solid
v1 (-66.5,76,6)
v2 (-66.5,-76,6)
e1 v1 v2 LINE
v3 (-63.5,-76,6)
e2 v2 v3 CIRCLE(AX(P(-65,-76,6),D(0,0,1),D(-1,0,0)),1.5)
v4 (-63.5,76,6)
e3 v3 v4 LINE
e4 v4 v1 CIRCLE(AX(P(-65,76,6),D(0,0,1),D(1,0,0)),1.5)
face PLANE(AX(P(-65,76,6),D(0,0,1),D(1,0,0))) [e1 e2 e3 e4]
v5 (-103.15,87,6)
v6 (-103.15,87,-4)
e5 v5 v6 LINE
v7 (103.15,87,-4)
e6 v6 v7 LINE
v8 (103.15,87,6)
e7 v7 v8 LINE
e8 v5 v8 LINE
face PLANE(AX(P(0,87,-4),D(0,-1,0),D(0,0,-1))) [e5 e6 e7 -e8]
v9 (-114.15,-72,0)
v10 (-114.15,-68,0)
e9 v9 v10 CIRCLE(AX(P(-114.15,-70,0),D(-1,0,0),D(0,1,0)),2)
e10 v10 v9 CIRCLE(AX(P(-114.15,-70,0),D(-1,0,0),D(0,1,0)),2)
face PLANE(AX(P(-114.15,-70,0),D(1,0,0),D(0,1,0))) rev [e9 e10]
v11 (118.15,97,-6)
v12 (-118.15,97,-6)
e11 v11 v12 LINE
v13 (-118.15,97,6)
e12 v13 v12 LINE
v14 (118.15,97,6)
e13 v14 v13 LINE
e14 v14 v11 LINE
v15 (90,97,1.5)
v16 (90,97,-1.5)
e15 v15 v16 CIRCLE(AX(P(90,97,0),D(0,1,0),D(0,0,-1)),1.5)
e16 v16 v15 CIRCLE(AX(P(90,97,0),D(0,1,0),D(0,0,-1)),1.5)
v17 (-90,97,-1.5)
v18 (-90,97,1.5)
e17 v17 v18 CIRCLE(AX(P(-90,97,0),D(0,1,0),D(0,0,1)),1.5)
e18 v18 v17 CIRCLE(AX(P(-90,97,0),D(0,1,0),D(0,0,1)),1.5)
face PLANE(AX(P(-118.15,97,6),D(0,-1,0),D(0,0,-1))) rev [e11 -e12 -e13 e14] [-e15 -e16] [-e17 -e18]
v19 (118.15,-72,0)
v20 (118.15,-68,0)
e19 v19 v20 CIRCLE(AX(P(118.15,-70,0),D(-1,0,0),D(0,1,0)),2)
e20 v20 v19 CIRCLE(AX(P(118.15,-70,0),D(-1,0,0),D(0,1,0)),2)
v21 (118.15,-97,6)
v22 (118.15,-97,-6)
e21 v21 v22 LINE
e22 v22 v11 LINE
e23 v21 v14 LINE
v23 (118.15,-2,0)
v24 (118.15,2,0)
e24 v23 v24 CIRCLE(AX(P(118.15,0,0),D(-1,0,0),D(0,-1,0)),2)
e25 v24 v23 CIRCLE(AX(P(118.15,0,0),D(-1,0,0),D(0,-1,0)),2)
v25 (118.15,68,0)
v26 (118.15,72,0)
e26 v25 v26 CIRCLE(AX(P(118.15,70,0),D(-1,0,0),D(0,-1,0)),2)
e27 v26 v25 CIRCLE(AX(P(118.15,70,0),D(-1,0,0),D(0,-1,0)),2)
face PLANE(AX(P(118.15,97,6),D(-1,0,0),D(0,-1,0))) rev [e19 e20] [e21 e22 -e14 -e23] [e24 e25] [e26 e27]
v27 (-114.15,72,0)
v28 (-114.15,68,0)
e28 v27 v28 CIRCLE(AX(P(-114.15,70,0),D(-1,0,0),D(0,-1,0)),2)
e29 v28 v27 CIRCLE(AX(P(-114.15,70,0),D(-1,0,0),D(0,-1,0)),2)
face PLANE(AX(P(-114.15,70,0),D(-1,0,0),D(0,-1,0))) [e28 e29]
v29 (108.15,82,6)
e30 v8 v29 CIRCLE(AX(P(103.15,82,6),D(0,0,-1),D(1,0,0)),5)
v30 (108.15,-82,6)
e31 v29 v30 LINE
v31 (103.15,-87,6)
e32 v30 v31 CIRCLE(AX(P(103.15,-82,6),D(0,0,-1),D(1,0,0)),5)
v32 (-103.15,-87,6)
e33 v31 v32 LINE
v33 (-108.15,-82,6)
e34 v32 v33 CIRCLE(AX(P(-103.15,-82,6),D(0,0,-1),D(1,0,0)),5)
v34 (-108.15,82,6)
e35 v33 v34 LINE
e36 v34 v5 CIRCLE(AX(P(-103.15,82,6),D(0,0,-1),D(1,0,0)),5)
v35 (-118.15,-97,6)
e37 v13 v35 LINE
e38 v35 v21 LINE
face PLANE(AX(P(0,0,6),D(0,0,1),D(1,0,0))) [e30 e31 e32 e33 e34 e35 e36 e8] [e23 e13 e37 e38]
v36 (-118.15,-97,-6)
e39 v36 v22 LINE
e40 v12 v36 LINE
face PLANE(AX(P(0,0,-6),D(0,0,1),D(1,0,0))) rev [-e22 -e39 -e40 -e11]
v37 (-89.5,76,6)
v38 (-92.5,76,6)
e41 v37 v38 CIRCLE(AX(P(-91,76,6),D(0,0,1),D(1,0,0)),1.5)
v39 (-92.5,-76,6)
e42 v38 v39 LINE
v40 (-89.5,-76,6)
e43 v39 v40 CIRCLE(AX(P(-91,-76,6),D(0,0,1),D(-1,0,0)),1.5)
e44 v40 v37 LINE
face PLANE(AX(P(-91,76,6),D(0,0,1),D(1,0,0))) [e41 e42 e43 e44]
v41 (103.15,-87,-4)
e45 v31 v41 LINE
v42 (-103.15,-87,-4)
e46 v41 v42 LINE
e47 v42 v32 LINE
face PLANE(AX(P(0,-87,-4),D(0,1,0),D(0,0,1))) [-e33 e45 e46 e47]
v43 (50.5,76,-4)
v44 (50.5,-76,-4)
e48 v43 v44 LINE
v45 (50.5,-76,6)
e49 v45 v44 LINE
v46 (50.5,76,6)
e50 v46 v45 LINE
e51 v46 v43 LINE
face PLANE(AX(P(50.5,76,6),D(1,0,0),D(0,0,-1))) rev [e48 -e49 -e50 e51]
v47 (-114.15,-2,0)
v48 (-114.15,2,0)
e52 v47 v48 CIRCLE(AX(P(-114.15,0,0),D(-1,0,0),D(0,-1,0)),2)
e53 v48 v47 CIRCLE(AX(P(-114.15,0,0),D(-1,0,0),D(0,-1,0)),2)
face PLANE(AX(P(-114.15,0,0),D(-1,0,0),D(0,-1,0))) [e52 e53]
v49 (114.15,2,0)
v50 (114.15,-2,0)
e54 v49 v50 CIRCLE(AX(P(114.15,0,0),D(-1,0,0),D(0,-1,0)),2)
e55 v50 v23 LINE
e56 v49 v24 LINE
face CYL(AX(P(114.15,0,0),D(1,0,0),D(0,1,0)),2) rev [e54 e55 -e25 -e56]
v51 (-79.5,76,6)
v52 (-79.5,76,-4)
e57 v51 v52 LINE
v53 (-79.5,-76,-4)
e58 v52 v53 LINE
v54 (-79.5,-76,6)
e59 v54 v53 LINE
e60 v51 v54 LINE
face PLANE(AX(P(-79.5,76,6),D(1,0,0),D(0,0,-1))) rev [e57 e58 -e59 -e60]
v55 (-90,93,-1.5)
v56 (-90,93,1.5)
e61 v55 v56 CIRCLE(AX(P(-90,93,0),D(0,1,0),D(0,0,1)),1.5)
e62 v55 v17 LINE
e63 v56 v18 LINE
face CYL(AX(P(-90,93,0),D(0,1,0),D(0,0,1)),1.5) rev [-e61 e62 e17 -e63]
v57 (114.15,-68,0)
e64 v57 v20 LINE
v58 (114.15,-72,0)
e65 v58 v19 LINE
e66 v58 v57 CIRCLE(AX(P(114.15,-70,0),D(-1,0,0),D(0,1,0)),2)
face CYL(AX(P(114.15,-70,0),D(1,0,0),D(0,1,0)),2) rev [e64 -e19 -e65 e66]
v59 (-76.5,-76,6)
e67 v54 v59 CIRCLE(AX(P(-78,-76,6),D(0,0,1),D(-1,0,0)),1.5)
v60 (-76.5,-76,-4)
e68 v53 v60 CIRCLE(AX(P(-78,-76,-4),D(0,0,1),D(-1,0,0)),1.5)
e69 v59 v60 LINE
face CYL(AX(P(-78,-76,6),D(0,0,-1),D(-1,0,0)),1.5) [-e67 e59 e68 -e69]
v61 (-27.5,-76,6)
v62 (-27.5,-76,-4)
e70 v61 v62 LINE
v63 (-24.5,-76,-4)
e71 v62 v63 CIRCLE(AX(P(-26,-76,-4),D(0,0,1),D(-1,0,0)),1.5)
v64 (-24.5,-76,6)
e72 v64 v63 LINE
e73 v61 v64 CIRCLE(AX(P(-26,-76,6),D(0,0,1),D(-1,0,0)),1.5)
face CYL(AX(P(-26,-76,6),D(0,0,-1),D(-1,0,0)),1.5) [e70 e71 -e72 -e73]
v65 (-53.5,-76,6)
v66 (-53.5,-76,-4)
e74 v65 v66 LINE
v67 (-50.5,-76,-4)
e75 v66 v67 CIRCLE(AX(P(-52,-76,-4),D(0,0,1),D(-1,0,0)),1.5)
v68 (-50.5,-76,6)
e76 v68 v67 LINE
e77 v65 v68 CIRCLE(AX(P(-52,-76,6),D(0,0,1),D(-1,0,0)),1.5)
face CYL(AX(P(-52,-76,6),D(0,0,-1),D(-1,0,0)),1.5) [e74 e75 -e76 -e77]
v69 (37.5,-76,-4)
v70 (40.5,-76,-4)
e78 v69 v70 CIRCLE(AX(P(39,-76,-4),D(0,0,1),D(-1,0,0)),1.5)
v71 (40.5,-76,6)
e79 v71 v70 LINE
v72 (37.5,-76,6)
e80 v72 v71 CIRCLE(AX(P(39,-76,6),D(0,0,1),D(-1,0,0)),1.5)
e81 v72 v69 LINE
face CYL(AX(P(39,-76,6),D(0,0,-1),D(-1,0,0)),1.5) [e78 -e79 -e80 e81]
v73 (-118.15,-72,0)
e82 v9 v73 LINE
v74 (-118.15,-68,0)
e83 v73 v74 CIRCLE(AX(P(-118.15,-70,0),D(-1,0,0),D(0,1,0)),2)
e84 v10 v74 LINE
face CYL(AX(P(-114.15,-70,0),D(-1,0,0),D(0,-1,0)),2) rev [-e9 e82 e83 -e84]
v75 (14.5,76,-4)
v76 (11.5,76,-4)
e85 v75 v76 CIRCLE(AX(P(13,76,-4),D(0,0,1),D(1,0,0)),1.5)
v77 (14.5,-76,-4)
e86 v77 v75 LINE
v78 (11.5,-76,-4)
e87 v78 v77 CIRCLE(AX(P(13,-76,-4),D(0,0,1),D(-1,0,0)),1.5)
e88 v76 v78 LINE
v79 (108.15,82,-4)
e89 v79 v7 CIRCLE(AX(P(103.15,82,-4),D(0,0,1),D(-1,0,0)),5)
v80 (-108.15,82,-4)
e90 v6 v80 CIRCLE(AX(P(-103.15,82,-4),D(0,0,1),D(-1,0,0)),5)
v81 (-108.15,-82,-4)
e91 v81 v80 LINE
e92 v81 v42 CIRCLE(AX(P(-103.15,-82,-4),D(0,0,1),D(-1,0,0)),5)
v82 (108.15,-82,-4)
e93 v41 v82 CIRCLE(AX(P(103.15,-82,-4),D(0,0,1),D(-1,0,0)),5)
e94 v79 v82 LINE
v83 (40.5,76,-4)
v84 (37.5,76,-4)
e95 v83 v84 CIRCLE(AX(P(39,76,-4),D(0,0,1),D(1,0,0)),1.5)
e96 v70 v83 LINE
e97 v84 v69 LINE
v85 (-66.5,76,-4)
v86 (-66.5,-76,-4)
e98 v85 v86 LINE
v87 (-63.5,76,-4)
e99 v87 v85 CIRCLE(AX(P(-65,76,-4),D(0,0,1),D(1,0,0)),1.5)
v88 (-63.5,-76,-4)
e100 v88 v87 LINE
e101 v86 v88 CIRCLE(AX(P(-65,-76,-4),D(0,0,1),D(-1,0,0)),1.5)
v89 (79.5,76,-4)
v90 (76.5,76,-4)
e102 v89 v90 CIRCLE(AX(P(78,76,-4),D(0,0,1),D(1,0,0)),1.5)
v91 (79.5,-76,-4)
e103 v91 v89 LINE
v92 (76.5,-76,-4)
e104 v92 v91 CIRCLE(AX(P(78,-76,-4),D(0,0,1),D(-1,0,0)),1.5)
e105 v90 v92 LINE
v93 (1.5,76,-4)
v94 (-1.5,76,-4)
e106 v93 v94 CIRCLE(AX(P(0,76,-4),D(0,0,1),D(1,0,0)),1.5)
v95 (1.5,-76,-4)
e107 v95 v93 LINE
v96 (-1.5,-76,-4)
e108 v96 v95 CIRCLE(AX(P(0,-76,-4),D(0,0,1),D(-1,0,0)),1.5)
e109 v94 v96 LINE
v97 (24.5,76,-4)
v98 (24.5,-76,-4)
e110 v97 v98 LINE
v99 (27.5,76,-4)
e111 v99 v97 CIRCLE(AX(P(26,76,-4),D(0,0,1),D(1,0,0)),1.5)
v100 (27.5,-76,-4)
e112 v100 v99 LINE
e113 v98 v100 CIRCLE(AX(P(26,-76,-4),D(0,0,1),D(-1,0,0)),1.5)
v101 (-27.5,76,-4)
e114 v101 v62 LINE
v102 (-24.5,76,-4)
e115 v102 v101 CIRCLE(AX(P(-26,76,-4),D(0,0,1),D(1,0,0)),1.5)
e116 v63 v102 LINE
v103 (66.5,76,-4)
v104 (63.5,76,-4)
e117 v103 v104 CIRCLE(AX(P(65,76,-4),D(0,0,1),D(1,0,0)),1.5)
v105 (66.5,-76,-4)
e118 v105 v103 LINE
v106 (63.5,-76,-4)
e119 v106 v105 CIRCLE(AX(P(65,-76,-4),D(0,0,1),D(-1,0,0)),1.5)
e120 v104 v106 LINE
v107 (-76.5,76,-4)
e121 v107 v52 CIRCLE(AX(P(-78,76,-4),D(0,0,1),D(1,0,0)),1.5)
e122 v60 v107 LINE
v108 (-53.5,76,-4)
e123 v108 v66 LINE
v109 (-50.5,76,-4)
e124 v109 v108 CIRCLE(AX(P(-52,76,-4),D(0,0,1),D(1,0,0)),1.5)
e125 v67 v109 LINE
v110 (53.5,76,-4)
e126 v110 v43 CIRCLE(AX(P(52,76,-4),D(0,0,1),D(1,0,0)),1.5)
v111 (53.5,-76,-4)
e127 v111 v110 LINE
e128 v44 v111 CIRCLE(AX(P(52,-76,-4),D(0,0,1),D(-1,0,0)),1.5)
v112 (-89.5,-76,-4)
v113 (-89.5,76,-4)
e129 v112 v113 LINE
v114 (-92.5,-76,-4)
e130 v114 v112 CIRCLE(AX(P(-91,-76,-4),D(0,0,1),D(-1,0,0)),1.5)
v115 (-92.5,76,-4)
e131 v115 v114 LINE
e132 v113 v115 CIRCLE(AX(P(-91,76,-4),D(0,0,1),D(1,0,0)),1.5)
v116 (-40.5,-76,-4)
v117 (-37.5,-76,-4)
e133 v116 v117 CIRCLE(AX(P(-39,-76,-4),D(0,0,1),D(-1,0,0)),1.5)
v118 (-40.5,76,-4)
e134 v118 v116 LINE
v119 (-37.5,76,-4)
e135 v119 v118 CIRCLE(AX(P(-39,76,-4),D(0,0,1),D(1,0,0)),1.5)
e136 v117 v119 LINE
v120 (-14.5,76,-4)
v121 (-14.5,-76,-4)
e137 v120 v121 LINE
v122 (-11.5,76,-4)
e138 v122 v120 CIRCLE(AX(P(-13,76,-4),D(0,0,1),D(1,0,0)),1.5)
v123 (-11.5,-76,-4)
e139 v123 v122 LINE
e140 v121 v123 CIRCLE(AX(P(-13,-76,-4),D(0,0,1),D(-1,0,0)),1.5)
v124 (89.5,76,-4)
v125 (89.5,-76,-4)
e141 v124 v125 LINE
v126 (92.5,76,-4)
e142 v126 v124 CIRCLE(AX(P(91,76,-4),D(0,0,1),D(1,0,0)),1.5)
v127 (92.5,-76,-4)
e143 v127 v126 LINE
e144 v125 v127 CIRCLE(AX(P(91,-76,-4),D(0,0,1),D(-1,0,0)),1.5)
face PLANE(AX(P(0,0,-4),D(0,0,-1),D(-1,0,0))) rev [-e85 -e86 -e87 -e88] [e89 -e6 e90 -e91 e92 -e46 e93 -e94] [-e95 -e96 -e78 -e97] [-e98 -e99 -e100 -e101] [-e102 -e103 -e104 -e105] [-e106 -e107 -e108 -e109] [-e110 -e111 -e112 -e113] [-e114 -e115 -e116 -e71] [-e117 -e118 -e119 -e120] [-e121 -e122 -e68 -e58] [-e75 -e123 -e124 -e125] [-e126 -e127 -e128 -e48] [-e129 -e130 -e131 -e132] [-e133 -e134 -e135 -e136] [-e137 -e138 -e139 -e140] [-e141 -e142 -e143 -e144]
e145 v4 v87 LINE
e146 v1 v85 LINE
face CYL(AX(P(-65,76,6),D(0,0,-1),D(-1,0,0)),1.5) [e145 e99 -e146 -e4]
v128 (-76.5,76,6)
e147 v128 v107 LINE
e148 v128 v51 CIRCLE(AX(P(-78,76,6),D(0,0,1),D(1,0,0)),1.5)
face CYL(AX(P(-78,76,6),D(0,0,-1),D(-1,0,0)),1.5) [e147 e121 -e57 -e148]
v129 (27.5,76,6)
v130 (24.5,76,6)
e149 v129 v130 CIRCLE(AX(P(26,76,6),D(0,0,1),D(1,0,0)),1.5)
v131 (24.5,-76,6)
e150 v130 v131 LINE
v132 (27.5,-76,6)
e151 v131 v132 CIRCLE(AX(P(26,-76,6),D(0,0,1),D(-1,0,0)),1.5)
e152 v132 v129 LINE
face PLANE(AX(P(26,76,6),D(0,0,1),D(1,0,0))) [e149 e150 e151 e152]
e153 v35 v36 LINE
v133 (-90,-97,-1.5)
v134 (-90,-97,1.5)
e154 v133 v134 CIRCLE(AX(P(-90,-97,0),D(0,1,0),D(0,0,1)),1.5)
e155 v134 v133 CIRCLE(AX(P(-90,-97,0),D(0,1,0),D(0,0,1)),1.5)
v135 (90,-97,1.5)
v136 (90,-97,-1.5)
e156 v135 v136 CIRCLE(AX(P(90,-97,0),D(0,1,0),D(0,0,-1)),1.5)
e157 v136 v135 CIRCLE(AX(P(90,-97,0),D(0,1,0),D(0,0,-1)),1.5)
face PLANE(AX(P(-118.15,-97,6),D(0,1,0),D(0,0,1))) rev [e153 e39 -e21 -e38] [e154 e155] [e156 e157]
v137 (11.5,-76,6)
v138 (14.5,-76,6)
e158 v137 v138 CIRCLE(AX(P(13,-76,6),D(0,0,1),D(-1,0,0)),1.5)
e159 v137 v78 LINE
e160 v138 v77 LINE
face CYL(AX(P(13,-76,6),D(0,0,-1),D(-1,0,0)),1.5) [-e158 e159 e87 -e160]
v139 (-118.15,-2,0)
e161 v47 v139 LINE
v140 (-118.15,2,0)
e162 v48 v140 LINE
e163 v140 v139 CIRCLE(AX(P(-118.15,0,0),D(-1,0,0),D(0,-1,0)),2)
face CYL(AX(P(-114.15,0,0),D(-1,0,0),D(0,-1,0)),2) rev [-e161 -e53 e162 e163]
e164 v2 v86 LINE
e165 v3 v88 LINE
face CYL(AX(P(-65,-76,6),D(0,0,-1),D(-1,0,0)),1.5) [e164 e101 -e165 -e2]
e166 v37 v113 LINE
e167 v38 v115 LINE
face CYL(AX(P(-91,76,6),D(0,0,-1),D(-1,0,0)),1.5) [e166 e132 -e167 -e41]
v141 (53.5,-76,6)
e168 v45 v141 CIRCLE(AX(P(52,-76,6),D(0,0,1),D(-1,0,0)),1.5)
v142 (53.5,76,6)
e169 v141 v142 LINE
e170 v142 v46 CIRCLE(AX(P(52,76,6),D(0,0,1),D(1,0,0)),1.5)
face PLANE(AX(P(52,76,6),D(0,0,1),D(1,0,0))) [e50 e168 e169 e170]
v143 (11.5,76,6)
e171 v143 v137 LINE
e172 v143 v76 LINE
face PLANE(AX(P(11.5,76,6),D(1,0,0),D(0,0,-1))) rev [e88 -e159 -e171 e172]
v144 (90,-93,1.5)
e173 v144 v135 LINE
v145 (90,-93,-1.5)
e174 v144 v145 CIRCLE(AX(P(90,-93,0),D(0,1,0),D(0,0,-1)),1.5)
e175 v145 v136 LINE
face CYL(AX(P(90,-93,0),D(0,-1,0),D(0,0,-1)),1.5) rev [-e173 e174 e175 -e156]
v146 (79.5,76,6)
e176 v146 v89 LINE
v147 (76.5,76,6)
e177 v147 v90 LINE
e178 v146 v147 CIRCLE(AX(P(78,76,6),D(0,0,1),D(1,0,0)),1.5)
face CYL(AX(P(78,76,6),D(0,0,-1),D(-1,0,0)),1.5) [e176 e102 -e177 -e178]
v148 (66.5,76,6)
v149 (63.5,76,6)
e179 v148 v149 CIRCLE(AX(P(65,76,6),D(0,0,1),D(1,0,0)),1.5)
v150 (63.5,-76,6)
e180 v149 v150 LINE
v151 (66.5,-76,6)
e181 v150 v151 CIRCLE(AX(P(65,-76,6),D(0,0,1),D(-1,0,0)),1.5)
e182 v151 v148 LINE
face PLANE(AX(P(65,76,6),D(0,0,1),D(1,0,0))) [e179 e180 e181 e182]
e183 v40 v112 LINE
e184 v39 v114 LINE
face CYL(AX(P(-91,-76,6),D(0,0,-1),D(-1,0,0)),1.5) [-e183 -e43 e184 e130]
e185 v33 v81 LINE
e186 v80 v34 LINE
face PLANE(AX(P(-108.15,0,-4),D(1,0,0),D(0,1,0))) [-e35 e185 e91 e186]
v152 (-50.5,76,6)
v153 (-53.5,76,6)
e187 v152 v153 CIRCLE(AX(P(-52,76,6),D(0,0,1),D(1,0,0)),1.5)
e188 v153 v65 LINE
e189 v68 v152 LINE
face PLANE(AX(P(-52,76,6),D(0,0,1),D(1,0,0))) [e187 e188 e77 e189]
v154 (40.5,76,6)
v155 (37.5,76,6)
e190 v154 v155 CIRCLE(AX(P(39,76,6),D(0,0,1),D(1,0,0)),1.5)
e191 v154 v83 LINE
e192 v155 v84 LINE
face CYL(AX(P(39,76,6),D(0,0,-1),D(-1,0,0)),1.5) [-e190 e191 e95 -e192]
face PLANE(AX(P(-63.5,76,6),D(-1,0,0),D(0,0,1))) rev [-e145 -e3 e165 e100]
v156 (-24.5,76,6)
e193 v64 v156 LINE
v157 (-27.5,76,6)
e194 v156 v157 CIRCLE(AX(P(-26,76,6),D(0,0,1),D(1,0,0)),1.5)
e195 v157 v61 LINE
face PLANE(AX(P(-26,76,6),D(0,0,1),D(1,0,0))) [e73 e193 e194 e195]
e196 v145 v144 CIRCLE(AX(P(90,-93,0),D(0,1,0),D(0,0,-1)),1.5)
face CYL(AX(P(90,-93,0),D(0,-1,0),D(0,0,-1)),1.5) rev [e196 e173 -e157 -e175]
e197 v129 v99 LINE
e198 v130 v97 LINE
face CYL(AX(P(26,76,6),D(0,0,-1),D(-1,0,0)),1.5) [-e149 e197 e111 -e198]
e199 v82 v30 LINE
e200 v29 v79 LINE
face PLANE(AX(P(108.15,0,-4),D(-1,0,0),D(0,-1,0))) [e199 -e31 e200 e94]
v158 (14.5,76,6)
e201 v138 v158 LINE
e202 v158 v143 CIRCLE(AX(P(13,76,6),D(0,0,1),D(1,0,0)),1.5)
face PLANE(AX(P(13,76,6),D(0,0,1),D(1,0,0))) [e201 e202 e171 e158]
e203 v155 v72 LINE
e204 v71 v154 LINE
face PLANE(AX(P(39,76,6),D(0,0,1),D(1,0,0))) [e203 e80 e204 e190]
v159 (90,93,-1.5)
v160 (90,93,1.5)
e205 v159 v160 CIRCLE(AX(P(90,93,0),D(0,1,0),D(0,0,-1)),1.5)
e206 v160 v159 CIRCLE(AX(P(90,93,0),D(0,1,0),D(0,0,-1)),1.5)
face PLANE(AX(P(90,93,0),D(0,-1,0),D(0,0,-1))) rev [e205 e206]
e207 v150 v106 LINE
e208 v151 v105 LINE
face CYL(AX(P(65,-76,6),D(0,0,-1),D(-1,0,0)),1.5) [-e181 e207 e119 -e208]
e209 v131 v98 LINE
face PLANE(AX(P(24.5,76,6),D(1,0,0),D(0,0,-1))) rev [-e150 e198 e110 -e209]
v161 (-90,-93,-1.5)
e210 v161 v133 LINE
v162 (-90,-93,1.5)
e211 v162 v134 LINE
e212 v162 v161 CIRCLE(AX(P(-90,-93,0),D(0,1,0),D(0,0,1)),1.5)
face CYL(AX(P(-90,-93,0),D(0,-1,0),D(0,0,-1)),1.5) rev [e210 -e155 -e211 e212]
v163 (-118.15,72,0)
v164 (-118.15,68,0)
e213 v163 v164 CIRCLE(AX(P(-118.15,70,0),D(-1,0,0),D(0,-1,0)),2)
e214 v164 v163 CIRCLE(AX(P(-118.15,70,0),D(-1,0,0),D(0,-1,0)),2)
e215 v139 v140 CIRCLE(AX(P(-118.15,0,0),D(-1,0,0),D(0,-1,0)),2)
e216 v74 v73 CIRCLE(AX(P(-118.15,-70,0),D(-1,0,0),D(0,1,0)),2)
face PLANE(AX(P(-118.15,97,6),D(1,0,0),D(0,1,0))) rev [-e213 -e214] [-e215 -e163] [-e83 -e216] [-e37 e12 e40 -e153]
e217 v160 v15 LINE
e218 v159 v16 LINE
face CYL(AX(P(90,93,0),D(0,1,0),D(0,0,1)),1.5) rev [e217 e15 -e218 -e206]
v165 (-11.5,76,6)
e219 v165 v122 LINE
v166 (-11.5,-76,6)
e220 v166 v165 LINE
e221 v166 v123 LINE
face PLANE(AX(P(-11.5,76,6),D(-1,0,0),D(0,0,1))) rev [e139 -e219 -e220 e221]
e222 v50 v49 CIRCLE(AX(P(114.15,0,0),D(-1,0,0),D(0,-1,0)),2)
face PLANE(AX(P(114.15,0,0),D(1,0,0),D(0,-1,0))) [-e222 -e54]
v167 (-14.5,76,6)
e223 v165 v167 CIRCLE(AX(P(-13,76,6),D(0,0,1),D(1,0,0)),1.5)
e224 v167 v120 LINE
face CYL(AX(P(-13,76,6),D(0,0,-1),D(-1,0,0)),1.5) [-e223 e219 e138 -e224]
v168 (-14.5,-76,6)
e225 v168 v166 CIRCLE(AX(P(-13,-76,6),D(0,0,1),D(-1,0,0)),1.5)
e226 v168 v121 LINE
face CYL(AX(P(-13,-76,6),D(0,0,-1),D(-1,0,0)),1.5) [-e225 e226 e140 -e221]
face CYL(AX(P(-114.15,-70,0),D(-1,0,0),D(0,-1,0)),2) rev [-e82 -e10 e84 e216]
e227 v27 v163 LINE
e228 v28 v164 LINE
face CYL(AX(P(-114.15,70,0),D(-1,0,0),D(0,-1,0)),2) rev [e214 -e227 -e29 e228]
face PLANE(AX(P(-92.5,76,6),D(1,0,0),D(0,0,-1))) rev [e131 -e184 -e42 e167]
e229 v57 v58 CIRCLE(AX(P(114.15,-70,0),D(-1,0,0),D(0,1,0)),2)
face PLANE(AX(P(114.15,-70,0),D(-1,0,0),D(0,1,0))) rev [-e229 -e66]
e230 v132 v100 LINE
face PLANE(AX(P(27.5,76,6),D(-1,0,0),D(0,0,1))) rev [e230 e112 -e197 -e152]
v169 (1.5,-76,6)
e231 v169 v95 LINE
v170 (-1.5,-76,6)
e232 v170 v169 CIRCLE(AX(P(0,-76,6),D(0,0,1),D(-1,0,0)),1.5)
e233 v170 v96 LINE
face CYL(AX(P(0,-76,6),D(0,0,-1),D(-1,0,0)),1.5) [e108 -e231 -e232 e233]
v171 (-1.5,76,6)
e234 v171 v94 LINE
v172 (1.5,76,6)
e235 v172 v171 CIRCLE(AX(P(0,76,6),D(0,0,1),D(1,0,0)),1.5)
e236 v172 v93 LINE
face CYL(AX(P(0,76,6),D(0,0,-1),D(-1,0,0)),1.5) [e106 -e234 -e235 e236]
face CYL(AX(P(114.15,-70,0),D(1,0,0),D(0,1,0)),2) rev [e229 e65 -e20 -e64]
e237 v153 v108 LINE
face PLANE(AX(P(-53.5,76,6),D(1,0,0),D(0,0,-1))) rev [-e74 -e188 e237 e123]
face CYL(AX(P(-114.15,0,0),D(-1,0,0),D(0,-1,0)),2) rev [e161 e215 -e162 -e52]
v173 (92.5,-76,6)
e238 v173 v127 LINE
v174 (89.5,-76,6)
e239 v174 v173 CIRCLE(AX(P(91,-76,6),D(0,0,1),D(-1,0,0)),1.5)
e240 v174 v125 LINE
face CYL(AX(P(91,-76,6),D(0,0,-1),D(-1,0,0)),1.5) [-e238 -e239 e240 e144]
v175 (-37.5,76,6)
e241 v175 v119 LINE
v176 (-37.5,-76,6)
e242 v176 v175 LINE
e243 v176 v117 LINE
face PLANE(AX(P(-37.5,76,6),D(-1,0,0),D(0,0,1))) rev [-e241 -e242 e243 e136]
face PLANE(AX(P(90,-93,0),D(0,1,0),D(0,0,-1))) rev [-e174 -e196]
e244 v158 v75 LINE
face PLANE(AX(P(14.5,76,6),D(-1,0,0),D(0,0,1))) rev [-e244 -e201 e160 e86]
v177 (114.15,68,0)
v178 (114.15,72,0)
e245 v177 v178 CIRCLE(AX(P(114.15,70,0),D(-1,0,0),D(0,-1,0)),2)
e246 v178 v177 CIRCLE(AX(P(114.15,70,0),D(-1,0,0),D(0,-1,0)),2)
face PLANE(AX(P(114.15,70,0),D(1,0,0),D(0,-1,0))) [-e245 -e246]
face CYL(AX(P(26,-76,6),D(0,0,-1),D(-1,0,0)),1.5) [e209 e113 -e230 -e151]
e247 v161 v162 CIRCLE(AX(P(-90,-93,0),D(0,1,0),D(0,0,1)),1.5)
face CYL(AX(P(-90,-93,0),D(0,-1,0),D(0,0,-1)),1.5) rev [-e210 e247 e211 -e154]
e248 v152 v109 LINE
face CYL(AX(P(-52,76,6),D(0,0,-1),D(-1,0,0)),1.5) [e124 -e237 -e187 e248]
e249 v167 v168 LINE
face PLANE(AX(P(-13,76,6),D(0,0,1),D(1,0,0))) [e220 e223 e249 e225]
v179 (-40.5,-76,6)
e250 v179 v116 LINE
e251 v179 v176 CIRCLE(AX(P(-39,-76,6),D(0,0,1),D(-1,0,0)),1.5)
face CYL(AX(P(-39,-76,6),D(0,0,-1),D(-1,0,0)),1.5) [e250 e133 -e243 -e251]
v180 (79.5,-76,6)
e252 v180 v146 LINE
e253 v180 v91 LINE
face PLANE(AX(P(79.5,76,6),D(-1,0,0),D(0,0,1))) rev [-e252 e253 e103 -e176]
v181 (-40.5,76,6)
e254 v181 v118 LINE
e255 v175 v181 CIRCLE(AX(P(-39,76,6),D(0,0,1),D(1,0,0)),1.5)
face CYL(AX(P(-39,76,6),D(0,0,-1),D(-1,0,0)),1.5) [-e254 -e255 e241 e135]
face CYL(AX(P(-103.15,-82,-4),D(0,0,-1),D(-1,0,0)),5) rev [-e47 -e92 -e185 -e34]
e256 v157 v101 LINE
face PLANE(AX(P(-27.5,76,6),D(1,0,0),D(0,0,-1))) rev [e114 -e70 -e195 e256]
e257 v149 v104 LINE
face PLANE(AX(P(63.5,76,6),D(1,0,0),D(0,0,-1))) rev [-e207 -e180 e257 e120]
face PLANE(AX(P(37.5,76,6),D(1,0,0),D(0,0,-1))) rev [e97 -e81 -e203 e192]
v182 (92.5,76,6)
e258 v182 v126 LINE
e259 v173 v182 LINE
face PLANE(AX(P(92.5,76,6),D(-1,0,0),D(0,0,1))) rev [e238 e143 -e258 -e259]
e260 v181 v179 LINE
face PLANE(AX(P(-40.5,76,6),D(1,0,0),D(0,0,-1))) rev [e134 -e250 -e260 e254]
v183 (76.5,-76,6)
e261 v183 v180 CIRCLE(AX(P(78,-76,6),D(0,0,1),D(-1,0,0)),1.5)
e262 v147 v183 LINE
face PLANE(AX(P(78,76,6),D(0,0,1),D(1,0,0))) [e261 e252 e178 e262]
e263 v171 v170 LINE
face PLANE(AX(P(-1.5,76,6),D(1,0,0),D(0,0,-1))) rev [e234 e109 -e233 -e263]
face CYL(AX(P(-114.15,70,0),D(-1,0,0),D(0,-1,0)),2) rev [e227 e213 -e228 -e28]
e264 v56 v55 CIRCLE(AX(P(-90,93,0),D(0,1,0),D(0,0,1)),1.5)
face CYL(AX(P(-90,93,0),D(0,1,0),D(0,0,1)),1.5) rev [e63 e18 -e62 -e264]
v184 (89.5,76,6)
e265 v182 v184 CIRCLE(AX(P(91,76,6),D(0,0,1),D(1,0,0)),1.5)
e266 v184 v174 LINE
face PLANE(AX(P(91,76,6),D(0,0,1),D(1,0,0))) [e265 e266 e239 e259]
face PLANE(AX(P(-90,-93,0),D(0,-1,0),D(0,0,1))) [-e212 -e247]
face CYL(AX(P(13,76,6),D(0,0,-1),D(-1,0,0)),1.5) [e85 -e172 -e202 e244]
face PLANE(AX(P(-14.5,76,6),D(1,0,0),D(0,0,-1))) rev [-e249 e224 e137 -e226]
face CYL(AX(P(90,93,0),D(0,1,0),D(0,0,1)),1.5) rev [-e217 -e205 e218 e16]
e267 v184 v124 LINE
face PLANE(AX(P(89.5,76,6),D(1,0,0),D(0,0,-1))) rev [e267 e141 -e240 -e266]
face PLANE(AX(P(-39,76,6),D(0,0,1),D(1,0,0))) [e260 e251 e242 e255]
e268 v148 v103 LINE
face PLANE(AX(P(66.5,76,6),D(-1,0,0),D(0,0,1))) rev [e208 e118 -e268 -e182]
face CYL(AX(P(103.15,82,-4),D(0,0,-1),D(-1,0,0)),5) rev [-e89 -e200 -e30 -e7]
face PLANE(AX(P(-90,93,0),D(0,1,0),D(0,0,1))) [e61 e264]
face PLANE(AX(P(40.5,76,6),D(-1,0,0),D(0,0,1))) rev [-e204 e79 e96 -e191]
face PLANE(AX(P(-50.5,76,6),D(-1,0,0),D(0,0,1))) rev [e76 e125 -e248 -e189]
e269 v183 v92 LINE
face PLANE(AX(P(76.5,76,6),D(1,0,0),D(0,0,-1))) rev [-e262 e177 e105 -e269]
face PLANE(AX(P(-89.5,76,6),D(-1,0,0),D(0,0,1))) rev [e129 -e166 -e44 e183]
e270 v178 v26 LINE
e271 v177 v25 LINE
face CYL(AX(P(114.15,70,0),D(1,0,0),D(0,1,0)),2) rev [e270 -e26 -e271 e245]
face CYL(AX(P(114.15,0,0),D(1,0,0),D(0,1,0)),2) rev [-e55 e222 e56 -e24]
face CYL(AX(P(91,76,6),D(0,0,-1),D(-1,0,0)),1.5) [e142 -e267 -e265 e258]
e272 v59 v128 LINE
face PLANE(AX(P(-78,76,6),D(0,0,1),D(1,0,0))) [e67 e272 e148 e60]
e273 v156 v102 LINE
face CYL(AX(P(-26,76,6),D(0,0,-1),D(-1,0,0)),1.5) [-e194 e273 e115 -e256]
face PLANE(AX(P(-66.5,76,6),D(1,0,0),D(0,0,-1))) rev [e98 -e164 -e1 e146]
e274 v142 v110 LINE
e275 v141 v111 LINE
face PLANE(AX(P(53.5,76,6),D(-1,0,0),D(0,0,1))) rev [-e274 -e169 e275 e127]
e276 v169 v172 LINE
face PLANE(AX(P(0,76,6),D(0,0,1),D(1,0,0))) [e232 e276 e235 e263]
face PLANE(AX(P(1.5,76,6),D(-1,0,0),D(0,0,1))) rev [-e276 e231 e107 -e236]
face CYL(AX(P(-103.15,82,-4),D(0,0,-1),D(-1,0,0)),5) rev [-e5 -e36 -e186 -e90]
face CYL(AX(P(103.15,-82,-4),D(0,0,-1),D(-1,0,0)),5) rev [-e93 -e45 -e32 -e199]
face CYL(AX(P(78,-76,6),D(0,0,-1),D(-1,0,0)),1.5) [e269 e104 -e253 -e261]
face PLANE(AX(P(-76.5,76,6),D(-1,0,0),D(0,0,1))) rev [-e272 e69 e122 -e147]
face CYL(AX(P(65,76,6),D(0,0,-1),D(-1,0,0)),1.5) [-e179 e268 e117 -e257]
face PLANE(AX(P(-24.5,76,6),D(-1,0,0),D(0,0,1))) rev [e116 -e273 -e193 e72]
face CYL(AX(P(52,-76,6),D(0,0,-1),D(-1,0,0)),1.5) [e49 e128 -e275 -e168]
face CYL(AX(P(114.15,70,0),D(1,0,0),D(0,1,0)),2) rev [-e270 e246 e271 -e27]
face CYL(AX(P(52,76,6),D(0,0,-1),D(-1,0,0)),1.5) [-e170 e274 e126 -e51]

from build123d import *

# Parameters (mm, degrees)
SKETCH1_W           = 236.3
SKETCH1_H           = 194
BOSS_EXTRUDE1_DEPTH = 6
SKETCH2_W           = 216.3
SKETCH2_H           = 174
CUT_EXTRUDE1_DEPTH  = 10
BOSS_EXTRUDE2_DEPTH = 10
LPATTERN1_COUNT     = 8
LPATTERN1_PITCH     = 13
LPATTERN1_COL_COUNT = 8
LPATTERN1_COL_PITCH = 13
SKETCH5_R           = 1.5
CUT_EXTRUDE2_DEPTH  = 4
SKETCH6_R           = 2
CUT_EXTRUDE3_DEPTH  = 4
FILLET1_R           = 5


with BuildPart() as part:
    # Sketch1 → Boss-Extrude1 (new, symmetric)
    with BuildSketch(Plane.XY):
        Rectangle(SKETCH1_W, SKETCH1_H)
    extrude(amount=BOSS_EXTRUDE1_DEPTH, both=True)

    # Sketch2 → Cut-Extrude1 (cut)
    with BuildSketch(Plane.XY.offset(6)):
        Rectangle(SKETCH2_W, SKETCH2_H)
    extrude(amount=-CUT_EXTRUDE1_DEPTH, mode=Mode.SUBTRACT)

    # Sketch3 → Boss-Extrude2 (add)
    with BuildSketch(Plane.XY.offset(-4)):
        with BuildLine():
            Line((-1.5, 76), (-1.5, -76))
            ThreePointArc((-1.5, -76), (0, -77.5), (1.5, -76))
            Line((1.5, -76), (1.5, 76))
            ThreePointArc((1.5, 76), (0, 77.5), (-1.5, 76))
        make_face()
    boss_extrude2 = extrude(amount=BOSS_EXTRUDE2_DEPTH)

    # LPattern1: Boss-Extrude2 ×8
    with Locations(*[(i * LPATTERN1_PITCH, 0, 0) for i in range(1, LPATTERN1_COUNT)]):
        add(boss_extrude2)

    # LPattern1 col: Boss-Extrude2 ×8
    with Locations(*[(-i * LPATTERN1_COL_PITCH, 0, 0) for i in range(1, LPATTERN1_COL_COUNT)]):
        add(boss_extrude2)

    # Sketch5 → Cut-Extrude2 (cut)
    with BuildSketch(Plane(origin=(0, 97, 0), x_dir=(1, 0, 0), z_dir=(0, 1, 0))):
        with Locations(Location((-90, 0, 0), (0, 0, 270))):
            Circle(SKETCH5_R)
        with Locations(Location((90, 0, 0), (0, 0, 90))):
            Circle(SKETCH5_R)
    cut_extrude2 = extrude(amount=-CUT_EXTRUDE2_DEPTH, mode=Mode.SUBTRACT)

    # Mirror1: Cut-Extrude2 across plane
    add(cut_extrude2.mirror(Plane.ZX), mode=Mode.SUBTRACT)

    # Sketch6 → Cut-Extrude3 (cut)
    with BuildSketch(Plane.ZY.offset(118.15)):
        with Locations(Location((0, 70, 0), (0, 0, 270))):
            Circle(SKETCH6_R)
        with Locations(Location((0, 0, 0), (0, 0, 270))):
            Circle(SKETCH6_R)
        with Locations(Location((0, -70, 0), (0, 0, 90))):
            Circle(SKETCH6_R)
    cut_extrude3 = extrude(amount=-CUT_EXTRUDE3_DEPTH, mode=Mode.SUBTRACT)

    # Mirror2: Cut-Extrude3 across plane
    add(cut_extrude3.mirror(Plane(origin=(0, 0, 0), x_dir=(0, 0, 1), z_dir=(1, 0, 0))), mode=Mode.SUBTRACT)

    # Fillet1
    fillet1_edges = [part.edges().sort_by_distance(p)[0] for p in [
        (-108.15, 87, 1),
        (108.15, 87, 1),
        (108.15, -87, 1),
        (-108.15, -87, 1),
    ]]
    fillet(fillet1_edges, radius=FILLET1_R)


solid = part.part
